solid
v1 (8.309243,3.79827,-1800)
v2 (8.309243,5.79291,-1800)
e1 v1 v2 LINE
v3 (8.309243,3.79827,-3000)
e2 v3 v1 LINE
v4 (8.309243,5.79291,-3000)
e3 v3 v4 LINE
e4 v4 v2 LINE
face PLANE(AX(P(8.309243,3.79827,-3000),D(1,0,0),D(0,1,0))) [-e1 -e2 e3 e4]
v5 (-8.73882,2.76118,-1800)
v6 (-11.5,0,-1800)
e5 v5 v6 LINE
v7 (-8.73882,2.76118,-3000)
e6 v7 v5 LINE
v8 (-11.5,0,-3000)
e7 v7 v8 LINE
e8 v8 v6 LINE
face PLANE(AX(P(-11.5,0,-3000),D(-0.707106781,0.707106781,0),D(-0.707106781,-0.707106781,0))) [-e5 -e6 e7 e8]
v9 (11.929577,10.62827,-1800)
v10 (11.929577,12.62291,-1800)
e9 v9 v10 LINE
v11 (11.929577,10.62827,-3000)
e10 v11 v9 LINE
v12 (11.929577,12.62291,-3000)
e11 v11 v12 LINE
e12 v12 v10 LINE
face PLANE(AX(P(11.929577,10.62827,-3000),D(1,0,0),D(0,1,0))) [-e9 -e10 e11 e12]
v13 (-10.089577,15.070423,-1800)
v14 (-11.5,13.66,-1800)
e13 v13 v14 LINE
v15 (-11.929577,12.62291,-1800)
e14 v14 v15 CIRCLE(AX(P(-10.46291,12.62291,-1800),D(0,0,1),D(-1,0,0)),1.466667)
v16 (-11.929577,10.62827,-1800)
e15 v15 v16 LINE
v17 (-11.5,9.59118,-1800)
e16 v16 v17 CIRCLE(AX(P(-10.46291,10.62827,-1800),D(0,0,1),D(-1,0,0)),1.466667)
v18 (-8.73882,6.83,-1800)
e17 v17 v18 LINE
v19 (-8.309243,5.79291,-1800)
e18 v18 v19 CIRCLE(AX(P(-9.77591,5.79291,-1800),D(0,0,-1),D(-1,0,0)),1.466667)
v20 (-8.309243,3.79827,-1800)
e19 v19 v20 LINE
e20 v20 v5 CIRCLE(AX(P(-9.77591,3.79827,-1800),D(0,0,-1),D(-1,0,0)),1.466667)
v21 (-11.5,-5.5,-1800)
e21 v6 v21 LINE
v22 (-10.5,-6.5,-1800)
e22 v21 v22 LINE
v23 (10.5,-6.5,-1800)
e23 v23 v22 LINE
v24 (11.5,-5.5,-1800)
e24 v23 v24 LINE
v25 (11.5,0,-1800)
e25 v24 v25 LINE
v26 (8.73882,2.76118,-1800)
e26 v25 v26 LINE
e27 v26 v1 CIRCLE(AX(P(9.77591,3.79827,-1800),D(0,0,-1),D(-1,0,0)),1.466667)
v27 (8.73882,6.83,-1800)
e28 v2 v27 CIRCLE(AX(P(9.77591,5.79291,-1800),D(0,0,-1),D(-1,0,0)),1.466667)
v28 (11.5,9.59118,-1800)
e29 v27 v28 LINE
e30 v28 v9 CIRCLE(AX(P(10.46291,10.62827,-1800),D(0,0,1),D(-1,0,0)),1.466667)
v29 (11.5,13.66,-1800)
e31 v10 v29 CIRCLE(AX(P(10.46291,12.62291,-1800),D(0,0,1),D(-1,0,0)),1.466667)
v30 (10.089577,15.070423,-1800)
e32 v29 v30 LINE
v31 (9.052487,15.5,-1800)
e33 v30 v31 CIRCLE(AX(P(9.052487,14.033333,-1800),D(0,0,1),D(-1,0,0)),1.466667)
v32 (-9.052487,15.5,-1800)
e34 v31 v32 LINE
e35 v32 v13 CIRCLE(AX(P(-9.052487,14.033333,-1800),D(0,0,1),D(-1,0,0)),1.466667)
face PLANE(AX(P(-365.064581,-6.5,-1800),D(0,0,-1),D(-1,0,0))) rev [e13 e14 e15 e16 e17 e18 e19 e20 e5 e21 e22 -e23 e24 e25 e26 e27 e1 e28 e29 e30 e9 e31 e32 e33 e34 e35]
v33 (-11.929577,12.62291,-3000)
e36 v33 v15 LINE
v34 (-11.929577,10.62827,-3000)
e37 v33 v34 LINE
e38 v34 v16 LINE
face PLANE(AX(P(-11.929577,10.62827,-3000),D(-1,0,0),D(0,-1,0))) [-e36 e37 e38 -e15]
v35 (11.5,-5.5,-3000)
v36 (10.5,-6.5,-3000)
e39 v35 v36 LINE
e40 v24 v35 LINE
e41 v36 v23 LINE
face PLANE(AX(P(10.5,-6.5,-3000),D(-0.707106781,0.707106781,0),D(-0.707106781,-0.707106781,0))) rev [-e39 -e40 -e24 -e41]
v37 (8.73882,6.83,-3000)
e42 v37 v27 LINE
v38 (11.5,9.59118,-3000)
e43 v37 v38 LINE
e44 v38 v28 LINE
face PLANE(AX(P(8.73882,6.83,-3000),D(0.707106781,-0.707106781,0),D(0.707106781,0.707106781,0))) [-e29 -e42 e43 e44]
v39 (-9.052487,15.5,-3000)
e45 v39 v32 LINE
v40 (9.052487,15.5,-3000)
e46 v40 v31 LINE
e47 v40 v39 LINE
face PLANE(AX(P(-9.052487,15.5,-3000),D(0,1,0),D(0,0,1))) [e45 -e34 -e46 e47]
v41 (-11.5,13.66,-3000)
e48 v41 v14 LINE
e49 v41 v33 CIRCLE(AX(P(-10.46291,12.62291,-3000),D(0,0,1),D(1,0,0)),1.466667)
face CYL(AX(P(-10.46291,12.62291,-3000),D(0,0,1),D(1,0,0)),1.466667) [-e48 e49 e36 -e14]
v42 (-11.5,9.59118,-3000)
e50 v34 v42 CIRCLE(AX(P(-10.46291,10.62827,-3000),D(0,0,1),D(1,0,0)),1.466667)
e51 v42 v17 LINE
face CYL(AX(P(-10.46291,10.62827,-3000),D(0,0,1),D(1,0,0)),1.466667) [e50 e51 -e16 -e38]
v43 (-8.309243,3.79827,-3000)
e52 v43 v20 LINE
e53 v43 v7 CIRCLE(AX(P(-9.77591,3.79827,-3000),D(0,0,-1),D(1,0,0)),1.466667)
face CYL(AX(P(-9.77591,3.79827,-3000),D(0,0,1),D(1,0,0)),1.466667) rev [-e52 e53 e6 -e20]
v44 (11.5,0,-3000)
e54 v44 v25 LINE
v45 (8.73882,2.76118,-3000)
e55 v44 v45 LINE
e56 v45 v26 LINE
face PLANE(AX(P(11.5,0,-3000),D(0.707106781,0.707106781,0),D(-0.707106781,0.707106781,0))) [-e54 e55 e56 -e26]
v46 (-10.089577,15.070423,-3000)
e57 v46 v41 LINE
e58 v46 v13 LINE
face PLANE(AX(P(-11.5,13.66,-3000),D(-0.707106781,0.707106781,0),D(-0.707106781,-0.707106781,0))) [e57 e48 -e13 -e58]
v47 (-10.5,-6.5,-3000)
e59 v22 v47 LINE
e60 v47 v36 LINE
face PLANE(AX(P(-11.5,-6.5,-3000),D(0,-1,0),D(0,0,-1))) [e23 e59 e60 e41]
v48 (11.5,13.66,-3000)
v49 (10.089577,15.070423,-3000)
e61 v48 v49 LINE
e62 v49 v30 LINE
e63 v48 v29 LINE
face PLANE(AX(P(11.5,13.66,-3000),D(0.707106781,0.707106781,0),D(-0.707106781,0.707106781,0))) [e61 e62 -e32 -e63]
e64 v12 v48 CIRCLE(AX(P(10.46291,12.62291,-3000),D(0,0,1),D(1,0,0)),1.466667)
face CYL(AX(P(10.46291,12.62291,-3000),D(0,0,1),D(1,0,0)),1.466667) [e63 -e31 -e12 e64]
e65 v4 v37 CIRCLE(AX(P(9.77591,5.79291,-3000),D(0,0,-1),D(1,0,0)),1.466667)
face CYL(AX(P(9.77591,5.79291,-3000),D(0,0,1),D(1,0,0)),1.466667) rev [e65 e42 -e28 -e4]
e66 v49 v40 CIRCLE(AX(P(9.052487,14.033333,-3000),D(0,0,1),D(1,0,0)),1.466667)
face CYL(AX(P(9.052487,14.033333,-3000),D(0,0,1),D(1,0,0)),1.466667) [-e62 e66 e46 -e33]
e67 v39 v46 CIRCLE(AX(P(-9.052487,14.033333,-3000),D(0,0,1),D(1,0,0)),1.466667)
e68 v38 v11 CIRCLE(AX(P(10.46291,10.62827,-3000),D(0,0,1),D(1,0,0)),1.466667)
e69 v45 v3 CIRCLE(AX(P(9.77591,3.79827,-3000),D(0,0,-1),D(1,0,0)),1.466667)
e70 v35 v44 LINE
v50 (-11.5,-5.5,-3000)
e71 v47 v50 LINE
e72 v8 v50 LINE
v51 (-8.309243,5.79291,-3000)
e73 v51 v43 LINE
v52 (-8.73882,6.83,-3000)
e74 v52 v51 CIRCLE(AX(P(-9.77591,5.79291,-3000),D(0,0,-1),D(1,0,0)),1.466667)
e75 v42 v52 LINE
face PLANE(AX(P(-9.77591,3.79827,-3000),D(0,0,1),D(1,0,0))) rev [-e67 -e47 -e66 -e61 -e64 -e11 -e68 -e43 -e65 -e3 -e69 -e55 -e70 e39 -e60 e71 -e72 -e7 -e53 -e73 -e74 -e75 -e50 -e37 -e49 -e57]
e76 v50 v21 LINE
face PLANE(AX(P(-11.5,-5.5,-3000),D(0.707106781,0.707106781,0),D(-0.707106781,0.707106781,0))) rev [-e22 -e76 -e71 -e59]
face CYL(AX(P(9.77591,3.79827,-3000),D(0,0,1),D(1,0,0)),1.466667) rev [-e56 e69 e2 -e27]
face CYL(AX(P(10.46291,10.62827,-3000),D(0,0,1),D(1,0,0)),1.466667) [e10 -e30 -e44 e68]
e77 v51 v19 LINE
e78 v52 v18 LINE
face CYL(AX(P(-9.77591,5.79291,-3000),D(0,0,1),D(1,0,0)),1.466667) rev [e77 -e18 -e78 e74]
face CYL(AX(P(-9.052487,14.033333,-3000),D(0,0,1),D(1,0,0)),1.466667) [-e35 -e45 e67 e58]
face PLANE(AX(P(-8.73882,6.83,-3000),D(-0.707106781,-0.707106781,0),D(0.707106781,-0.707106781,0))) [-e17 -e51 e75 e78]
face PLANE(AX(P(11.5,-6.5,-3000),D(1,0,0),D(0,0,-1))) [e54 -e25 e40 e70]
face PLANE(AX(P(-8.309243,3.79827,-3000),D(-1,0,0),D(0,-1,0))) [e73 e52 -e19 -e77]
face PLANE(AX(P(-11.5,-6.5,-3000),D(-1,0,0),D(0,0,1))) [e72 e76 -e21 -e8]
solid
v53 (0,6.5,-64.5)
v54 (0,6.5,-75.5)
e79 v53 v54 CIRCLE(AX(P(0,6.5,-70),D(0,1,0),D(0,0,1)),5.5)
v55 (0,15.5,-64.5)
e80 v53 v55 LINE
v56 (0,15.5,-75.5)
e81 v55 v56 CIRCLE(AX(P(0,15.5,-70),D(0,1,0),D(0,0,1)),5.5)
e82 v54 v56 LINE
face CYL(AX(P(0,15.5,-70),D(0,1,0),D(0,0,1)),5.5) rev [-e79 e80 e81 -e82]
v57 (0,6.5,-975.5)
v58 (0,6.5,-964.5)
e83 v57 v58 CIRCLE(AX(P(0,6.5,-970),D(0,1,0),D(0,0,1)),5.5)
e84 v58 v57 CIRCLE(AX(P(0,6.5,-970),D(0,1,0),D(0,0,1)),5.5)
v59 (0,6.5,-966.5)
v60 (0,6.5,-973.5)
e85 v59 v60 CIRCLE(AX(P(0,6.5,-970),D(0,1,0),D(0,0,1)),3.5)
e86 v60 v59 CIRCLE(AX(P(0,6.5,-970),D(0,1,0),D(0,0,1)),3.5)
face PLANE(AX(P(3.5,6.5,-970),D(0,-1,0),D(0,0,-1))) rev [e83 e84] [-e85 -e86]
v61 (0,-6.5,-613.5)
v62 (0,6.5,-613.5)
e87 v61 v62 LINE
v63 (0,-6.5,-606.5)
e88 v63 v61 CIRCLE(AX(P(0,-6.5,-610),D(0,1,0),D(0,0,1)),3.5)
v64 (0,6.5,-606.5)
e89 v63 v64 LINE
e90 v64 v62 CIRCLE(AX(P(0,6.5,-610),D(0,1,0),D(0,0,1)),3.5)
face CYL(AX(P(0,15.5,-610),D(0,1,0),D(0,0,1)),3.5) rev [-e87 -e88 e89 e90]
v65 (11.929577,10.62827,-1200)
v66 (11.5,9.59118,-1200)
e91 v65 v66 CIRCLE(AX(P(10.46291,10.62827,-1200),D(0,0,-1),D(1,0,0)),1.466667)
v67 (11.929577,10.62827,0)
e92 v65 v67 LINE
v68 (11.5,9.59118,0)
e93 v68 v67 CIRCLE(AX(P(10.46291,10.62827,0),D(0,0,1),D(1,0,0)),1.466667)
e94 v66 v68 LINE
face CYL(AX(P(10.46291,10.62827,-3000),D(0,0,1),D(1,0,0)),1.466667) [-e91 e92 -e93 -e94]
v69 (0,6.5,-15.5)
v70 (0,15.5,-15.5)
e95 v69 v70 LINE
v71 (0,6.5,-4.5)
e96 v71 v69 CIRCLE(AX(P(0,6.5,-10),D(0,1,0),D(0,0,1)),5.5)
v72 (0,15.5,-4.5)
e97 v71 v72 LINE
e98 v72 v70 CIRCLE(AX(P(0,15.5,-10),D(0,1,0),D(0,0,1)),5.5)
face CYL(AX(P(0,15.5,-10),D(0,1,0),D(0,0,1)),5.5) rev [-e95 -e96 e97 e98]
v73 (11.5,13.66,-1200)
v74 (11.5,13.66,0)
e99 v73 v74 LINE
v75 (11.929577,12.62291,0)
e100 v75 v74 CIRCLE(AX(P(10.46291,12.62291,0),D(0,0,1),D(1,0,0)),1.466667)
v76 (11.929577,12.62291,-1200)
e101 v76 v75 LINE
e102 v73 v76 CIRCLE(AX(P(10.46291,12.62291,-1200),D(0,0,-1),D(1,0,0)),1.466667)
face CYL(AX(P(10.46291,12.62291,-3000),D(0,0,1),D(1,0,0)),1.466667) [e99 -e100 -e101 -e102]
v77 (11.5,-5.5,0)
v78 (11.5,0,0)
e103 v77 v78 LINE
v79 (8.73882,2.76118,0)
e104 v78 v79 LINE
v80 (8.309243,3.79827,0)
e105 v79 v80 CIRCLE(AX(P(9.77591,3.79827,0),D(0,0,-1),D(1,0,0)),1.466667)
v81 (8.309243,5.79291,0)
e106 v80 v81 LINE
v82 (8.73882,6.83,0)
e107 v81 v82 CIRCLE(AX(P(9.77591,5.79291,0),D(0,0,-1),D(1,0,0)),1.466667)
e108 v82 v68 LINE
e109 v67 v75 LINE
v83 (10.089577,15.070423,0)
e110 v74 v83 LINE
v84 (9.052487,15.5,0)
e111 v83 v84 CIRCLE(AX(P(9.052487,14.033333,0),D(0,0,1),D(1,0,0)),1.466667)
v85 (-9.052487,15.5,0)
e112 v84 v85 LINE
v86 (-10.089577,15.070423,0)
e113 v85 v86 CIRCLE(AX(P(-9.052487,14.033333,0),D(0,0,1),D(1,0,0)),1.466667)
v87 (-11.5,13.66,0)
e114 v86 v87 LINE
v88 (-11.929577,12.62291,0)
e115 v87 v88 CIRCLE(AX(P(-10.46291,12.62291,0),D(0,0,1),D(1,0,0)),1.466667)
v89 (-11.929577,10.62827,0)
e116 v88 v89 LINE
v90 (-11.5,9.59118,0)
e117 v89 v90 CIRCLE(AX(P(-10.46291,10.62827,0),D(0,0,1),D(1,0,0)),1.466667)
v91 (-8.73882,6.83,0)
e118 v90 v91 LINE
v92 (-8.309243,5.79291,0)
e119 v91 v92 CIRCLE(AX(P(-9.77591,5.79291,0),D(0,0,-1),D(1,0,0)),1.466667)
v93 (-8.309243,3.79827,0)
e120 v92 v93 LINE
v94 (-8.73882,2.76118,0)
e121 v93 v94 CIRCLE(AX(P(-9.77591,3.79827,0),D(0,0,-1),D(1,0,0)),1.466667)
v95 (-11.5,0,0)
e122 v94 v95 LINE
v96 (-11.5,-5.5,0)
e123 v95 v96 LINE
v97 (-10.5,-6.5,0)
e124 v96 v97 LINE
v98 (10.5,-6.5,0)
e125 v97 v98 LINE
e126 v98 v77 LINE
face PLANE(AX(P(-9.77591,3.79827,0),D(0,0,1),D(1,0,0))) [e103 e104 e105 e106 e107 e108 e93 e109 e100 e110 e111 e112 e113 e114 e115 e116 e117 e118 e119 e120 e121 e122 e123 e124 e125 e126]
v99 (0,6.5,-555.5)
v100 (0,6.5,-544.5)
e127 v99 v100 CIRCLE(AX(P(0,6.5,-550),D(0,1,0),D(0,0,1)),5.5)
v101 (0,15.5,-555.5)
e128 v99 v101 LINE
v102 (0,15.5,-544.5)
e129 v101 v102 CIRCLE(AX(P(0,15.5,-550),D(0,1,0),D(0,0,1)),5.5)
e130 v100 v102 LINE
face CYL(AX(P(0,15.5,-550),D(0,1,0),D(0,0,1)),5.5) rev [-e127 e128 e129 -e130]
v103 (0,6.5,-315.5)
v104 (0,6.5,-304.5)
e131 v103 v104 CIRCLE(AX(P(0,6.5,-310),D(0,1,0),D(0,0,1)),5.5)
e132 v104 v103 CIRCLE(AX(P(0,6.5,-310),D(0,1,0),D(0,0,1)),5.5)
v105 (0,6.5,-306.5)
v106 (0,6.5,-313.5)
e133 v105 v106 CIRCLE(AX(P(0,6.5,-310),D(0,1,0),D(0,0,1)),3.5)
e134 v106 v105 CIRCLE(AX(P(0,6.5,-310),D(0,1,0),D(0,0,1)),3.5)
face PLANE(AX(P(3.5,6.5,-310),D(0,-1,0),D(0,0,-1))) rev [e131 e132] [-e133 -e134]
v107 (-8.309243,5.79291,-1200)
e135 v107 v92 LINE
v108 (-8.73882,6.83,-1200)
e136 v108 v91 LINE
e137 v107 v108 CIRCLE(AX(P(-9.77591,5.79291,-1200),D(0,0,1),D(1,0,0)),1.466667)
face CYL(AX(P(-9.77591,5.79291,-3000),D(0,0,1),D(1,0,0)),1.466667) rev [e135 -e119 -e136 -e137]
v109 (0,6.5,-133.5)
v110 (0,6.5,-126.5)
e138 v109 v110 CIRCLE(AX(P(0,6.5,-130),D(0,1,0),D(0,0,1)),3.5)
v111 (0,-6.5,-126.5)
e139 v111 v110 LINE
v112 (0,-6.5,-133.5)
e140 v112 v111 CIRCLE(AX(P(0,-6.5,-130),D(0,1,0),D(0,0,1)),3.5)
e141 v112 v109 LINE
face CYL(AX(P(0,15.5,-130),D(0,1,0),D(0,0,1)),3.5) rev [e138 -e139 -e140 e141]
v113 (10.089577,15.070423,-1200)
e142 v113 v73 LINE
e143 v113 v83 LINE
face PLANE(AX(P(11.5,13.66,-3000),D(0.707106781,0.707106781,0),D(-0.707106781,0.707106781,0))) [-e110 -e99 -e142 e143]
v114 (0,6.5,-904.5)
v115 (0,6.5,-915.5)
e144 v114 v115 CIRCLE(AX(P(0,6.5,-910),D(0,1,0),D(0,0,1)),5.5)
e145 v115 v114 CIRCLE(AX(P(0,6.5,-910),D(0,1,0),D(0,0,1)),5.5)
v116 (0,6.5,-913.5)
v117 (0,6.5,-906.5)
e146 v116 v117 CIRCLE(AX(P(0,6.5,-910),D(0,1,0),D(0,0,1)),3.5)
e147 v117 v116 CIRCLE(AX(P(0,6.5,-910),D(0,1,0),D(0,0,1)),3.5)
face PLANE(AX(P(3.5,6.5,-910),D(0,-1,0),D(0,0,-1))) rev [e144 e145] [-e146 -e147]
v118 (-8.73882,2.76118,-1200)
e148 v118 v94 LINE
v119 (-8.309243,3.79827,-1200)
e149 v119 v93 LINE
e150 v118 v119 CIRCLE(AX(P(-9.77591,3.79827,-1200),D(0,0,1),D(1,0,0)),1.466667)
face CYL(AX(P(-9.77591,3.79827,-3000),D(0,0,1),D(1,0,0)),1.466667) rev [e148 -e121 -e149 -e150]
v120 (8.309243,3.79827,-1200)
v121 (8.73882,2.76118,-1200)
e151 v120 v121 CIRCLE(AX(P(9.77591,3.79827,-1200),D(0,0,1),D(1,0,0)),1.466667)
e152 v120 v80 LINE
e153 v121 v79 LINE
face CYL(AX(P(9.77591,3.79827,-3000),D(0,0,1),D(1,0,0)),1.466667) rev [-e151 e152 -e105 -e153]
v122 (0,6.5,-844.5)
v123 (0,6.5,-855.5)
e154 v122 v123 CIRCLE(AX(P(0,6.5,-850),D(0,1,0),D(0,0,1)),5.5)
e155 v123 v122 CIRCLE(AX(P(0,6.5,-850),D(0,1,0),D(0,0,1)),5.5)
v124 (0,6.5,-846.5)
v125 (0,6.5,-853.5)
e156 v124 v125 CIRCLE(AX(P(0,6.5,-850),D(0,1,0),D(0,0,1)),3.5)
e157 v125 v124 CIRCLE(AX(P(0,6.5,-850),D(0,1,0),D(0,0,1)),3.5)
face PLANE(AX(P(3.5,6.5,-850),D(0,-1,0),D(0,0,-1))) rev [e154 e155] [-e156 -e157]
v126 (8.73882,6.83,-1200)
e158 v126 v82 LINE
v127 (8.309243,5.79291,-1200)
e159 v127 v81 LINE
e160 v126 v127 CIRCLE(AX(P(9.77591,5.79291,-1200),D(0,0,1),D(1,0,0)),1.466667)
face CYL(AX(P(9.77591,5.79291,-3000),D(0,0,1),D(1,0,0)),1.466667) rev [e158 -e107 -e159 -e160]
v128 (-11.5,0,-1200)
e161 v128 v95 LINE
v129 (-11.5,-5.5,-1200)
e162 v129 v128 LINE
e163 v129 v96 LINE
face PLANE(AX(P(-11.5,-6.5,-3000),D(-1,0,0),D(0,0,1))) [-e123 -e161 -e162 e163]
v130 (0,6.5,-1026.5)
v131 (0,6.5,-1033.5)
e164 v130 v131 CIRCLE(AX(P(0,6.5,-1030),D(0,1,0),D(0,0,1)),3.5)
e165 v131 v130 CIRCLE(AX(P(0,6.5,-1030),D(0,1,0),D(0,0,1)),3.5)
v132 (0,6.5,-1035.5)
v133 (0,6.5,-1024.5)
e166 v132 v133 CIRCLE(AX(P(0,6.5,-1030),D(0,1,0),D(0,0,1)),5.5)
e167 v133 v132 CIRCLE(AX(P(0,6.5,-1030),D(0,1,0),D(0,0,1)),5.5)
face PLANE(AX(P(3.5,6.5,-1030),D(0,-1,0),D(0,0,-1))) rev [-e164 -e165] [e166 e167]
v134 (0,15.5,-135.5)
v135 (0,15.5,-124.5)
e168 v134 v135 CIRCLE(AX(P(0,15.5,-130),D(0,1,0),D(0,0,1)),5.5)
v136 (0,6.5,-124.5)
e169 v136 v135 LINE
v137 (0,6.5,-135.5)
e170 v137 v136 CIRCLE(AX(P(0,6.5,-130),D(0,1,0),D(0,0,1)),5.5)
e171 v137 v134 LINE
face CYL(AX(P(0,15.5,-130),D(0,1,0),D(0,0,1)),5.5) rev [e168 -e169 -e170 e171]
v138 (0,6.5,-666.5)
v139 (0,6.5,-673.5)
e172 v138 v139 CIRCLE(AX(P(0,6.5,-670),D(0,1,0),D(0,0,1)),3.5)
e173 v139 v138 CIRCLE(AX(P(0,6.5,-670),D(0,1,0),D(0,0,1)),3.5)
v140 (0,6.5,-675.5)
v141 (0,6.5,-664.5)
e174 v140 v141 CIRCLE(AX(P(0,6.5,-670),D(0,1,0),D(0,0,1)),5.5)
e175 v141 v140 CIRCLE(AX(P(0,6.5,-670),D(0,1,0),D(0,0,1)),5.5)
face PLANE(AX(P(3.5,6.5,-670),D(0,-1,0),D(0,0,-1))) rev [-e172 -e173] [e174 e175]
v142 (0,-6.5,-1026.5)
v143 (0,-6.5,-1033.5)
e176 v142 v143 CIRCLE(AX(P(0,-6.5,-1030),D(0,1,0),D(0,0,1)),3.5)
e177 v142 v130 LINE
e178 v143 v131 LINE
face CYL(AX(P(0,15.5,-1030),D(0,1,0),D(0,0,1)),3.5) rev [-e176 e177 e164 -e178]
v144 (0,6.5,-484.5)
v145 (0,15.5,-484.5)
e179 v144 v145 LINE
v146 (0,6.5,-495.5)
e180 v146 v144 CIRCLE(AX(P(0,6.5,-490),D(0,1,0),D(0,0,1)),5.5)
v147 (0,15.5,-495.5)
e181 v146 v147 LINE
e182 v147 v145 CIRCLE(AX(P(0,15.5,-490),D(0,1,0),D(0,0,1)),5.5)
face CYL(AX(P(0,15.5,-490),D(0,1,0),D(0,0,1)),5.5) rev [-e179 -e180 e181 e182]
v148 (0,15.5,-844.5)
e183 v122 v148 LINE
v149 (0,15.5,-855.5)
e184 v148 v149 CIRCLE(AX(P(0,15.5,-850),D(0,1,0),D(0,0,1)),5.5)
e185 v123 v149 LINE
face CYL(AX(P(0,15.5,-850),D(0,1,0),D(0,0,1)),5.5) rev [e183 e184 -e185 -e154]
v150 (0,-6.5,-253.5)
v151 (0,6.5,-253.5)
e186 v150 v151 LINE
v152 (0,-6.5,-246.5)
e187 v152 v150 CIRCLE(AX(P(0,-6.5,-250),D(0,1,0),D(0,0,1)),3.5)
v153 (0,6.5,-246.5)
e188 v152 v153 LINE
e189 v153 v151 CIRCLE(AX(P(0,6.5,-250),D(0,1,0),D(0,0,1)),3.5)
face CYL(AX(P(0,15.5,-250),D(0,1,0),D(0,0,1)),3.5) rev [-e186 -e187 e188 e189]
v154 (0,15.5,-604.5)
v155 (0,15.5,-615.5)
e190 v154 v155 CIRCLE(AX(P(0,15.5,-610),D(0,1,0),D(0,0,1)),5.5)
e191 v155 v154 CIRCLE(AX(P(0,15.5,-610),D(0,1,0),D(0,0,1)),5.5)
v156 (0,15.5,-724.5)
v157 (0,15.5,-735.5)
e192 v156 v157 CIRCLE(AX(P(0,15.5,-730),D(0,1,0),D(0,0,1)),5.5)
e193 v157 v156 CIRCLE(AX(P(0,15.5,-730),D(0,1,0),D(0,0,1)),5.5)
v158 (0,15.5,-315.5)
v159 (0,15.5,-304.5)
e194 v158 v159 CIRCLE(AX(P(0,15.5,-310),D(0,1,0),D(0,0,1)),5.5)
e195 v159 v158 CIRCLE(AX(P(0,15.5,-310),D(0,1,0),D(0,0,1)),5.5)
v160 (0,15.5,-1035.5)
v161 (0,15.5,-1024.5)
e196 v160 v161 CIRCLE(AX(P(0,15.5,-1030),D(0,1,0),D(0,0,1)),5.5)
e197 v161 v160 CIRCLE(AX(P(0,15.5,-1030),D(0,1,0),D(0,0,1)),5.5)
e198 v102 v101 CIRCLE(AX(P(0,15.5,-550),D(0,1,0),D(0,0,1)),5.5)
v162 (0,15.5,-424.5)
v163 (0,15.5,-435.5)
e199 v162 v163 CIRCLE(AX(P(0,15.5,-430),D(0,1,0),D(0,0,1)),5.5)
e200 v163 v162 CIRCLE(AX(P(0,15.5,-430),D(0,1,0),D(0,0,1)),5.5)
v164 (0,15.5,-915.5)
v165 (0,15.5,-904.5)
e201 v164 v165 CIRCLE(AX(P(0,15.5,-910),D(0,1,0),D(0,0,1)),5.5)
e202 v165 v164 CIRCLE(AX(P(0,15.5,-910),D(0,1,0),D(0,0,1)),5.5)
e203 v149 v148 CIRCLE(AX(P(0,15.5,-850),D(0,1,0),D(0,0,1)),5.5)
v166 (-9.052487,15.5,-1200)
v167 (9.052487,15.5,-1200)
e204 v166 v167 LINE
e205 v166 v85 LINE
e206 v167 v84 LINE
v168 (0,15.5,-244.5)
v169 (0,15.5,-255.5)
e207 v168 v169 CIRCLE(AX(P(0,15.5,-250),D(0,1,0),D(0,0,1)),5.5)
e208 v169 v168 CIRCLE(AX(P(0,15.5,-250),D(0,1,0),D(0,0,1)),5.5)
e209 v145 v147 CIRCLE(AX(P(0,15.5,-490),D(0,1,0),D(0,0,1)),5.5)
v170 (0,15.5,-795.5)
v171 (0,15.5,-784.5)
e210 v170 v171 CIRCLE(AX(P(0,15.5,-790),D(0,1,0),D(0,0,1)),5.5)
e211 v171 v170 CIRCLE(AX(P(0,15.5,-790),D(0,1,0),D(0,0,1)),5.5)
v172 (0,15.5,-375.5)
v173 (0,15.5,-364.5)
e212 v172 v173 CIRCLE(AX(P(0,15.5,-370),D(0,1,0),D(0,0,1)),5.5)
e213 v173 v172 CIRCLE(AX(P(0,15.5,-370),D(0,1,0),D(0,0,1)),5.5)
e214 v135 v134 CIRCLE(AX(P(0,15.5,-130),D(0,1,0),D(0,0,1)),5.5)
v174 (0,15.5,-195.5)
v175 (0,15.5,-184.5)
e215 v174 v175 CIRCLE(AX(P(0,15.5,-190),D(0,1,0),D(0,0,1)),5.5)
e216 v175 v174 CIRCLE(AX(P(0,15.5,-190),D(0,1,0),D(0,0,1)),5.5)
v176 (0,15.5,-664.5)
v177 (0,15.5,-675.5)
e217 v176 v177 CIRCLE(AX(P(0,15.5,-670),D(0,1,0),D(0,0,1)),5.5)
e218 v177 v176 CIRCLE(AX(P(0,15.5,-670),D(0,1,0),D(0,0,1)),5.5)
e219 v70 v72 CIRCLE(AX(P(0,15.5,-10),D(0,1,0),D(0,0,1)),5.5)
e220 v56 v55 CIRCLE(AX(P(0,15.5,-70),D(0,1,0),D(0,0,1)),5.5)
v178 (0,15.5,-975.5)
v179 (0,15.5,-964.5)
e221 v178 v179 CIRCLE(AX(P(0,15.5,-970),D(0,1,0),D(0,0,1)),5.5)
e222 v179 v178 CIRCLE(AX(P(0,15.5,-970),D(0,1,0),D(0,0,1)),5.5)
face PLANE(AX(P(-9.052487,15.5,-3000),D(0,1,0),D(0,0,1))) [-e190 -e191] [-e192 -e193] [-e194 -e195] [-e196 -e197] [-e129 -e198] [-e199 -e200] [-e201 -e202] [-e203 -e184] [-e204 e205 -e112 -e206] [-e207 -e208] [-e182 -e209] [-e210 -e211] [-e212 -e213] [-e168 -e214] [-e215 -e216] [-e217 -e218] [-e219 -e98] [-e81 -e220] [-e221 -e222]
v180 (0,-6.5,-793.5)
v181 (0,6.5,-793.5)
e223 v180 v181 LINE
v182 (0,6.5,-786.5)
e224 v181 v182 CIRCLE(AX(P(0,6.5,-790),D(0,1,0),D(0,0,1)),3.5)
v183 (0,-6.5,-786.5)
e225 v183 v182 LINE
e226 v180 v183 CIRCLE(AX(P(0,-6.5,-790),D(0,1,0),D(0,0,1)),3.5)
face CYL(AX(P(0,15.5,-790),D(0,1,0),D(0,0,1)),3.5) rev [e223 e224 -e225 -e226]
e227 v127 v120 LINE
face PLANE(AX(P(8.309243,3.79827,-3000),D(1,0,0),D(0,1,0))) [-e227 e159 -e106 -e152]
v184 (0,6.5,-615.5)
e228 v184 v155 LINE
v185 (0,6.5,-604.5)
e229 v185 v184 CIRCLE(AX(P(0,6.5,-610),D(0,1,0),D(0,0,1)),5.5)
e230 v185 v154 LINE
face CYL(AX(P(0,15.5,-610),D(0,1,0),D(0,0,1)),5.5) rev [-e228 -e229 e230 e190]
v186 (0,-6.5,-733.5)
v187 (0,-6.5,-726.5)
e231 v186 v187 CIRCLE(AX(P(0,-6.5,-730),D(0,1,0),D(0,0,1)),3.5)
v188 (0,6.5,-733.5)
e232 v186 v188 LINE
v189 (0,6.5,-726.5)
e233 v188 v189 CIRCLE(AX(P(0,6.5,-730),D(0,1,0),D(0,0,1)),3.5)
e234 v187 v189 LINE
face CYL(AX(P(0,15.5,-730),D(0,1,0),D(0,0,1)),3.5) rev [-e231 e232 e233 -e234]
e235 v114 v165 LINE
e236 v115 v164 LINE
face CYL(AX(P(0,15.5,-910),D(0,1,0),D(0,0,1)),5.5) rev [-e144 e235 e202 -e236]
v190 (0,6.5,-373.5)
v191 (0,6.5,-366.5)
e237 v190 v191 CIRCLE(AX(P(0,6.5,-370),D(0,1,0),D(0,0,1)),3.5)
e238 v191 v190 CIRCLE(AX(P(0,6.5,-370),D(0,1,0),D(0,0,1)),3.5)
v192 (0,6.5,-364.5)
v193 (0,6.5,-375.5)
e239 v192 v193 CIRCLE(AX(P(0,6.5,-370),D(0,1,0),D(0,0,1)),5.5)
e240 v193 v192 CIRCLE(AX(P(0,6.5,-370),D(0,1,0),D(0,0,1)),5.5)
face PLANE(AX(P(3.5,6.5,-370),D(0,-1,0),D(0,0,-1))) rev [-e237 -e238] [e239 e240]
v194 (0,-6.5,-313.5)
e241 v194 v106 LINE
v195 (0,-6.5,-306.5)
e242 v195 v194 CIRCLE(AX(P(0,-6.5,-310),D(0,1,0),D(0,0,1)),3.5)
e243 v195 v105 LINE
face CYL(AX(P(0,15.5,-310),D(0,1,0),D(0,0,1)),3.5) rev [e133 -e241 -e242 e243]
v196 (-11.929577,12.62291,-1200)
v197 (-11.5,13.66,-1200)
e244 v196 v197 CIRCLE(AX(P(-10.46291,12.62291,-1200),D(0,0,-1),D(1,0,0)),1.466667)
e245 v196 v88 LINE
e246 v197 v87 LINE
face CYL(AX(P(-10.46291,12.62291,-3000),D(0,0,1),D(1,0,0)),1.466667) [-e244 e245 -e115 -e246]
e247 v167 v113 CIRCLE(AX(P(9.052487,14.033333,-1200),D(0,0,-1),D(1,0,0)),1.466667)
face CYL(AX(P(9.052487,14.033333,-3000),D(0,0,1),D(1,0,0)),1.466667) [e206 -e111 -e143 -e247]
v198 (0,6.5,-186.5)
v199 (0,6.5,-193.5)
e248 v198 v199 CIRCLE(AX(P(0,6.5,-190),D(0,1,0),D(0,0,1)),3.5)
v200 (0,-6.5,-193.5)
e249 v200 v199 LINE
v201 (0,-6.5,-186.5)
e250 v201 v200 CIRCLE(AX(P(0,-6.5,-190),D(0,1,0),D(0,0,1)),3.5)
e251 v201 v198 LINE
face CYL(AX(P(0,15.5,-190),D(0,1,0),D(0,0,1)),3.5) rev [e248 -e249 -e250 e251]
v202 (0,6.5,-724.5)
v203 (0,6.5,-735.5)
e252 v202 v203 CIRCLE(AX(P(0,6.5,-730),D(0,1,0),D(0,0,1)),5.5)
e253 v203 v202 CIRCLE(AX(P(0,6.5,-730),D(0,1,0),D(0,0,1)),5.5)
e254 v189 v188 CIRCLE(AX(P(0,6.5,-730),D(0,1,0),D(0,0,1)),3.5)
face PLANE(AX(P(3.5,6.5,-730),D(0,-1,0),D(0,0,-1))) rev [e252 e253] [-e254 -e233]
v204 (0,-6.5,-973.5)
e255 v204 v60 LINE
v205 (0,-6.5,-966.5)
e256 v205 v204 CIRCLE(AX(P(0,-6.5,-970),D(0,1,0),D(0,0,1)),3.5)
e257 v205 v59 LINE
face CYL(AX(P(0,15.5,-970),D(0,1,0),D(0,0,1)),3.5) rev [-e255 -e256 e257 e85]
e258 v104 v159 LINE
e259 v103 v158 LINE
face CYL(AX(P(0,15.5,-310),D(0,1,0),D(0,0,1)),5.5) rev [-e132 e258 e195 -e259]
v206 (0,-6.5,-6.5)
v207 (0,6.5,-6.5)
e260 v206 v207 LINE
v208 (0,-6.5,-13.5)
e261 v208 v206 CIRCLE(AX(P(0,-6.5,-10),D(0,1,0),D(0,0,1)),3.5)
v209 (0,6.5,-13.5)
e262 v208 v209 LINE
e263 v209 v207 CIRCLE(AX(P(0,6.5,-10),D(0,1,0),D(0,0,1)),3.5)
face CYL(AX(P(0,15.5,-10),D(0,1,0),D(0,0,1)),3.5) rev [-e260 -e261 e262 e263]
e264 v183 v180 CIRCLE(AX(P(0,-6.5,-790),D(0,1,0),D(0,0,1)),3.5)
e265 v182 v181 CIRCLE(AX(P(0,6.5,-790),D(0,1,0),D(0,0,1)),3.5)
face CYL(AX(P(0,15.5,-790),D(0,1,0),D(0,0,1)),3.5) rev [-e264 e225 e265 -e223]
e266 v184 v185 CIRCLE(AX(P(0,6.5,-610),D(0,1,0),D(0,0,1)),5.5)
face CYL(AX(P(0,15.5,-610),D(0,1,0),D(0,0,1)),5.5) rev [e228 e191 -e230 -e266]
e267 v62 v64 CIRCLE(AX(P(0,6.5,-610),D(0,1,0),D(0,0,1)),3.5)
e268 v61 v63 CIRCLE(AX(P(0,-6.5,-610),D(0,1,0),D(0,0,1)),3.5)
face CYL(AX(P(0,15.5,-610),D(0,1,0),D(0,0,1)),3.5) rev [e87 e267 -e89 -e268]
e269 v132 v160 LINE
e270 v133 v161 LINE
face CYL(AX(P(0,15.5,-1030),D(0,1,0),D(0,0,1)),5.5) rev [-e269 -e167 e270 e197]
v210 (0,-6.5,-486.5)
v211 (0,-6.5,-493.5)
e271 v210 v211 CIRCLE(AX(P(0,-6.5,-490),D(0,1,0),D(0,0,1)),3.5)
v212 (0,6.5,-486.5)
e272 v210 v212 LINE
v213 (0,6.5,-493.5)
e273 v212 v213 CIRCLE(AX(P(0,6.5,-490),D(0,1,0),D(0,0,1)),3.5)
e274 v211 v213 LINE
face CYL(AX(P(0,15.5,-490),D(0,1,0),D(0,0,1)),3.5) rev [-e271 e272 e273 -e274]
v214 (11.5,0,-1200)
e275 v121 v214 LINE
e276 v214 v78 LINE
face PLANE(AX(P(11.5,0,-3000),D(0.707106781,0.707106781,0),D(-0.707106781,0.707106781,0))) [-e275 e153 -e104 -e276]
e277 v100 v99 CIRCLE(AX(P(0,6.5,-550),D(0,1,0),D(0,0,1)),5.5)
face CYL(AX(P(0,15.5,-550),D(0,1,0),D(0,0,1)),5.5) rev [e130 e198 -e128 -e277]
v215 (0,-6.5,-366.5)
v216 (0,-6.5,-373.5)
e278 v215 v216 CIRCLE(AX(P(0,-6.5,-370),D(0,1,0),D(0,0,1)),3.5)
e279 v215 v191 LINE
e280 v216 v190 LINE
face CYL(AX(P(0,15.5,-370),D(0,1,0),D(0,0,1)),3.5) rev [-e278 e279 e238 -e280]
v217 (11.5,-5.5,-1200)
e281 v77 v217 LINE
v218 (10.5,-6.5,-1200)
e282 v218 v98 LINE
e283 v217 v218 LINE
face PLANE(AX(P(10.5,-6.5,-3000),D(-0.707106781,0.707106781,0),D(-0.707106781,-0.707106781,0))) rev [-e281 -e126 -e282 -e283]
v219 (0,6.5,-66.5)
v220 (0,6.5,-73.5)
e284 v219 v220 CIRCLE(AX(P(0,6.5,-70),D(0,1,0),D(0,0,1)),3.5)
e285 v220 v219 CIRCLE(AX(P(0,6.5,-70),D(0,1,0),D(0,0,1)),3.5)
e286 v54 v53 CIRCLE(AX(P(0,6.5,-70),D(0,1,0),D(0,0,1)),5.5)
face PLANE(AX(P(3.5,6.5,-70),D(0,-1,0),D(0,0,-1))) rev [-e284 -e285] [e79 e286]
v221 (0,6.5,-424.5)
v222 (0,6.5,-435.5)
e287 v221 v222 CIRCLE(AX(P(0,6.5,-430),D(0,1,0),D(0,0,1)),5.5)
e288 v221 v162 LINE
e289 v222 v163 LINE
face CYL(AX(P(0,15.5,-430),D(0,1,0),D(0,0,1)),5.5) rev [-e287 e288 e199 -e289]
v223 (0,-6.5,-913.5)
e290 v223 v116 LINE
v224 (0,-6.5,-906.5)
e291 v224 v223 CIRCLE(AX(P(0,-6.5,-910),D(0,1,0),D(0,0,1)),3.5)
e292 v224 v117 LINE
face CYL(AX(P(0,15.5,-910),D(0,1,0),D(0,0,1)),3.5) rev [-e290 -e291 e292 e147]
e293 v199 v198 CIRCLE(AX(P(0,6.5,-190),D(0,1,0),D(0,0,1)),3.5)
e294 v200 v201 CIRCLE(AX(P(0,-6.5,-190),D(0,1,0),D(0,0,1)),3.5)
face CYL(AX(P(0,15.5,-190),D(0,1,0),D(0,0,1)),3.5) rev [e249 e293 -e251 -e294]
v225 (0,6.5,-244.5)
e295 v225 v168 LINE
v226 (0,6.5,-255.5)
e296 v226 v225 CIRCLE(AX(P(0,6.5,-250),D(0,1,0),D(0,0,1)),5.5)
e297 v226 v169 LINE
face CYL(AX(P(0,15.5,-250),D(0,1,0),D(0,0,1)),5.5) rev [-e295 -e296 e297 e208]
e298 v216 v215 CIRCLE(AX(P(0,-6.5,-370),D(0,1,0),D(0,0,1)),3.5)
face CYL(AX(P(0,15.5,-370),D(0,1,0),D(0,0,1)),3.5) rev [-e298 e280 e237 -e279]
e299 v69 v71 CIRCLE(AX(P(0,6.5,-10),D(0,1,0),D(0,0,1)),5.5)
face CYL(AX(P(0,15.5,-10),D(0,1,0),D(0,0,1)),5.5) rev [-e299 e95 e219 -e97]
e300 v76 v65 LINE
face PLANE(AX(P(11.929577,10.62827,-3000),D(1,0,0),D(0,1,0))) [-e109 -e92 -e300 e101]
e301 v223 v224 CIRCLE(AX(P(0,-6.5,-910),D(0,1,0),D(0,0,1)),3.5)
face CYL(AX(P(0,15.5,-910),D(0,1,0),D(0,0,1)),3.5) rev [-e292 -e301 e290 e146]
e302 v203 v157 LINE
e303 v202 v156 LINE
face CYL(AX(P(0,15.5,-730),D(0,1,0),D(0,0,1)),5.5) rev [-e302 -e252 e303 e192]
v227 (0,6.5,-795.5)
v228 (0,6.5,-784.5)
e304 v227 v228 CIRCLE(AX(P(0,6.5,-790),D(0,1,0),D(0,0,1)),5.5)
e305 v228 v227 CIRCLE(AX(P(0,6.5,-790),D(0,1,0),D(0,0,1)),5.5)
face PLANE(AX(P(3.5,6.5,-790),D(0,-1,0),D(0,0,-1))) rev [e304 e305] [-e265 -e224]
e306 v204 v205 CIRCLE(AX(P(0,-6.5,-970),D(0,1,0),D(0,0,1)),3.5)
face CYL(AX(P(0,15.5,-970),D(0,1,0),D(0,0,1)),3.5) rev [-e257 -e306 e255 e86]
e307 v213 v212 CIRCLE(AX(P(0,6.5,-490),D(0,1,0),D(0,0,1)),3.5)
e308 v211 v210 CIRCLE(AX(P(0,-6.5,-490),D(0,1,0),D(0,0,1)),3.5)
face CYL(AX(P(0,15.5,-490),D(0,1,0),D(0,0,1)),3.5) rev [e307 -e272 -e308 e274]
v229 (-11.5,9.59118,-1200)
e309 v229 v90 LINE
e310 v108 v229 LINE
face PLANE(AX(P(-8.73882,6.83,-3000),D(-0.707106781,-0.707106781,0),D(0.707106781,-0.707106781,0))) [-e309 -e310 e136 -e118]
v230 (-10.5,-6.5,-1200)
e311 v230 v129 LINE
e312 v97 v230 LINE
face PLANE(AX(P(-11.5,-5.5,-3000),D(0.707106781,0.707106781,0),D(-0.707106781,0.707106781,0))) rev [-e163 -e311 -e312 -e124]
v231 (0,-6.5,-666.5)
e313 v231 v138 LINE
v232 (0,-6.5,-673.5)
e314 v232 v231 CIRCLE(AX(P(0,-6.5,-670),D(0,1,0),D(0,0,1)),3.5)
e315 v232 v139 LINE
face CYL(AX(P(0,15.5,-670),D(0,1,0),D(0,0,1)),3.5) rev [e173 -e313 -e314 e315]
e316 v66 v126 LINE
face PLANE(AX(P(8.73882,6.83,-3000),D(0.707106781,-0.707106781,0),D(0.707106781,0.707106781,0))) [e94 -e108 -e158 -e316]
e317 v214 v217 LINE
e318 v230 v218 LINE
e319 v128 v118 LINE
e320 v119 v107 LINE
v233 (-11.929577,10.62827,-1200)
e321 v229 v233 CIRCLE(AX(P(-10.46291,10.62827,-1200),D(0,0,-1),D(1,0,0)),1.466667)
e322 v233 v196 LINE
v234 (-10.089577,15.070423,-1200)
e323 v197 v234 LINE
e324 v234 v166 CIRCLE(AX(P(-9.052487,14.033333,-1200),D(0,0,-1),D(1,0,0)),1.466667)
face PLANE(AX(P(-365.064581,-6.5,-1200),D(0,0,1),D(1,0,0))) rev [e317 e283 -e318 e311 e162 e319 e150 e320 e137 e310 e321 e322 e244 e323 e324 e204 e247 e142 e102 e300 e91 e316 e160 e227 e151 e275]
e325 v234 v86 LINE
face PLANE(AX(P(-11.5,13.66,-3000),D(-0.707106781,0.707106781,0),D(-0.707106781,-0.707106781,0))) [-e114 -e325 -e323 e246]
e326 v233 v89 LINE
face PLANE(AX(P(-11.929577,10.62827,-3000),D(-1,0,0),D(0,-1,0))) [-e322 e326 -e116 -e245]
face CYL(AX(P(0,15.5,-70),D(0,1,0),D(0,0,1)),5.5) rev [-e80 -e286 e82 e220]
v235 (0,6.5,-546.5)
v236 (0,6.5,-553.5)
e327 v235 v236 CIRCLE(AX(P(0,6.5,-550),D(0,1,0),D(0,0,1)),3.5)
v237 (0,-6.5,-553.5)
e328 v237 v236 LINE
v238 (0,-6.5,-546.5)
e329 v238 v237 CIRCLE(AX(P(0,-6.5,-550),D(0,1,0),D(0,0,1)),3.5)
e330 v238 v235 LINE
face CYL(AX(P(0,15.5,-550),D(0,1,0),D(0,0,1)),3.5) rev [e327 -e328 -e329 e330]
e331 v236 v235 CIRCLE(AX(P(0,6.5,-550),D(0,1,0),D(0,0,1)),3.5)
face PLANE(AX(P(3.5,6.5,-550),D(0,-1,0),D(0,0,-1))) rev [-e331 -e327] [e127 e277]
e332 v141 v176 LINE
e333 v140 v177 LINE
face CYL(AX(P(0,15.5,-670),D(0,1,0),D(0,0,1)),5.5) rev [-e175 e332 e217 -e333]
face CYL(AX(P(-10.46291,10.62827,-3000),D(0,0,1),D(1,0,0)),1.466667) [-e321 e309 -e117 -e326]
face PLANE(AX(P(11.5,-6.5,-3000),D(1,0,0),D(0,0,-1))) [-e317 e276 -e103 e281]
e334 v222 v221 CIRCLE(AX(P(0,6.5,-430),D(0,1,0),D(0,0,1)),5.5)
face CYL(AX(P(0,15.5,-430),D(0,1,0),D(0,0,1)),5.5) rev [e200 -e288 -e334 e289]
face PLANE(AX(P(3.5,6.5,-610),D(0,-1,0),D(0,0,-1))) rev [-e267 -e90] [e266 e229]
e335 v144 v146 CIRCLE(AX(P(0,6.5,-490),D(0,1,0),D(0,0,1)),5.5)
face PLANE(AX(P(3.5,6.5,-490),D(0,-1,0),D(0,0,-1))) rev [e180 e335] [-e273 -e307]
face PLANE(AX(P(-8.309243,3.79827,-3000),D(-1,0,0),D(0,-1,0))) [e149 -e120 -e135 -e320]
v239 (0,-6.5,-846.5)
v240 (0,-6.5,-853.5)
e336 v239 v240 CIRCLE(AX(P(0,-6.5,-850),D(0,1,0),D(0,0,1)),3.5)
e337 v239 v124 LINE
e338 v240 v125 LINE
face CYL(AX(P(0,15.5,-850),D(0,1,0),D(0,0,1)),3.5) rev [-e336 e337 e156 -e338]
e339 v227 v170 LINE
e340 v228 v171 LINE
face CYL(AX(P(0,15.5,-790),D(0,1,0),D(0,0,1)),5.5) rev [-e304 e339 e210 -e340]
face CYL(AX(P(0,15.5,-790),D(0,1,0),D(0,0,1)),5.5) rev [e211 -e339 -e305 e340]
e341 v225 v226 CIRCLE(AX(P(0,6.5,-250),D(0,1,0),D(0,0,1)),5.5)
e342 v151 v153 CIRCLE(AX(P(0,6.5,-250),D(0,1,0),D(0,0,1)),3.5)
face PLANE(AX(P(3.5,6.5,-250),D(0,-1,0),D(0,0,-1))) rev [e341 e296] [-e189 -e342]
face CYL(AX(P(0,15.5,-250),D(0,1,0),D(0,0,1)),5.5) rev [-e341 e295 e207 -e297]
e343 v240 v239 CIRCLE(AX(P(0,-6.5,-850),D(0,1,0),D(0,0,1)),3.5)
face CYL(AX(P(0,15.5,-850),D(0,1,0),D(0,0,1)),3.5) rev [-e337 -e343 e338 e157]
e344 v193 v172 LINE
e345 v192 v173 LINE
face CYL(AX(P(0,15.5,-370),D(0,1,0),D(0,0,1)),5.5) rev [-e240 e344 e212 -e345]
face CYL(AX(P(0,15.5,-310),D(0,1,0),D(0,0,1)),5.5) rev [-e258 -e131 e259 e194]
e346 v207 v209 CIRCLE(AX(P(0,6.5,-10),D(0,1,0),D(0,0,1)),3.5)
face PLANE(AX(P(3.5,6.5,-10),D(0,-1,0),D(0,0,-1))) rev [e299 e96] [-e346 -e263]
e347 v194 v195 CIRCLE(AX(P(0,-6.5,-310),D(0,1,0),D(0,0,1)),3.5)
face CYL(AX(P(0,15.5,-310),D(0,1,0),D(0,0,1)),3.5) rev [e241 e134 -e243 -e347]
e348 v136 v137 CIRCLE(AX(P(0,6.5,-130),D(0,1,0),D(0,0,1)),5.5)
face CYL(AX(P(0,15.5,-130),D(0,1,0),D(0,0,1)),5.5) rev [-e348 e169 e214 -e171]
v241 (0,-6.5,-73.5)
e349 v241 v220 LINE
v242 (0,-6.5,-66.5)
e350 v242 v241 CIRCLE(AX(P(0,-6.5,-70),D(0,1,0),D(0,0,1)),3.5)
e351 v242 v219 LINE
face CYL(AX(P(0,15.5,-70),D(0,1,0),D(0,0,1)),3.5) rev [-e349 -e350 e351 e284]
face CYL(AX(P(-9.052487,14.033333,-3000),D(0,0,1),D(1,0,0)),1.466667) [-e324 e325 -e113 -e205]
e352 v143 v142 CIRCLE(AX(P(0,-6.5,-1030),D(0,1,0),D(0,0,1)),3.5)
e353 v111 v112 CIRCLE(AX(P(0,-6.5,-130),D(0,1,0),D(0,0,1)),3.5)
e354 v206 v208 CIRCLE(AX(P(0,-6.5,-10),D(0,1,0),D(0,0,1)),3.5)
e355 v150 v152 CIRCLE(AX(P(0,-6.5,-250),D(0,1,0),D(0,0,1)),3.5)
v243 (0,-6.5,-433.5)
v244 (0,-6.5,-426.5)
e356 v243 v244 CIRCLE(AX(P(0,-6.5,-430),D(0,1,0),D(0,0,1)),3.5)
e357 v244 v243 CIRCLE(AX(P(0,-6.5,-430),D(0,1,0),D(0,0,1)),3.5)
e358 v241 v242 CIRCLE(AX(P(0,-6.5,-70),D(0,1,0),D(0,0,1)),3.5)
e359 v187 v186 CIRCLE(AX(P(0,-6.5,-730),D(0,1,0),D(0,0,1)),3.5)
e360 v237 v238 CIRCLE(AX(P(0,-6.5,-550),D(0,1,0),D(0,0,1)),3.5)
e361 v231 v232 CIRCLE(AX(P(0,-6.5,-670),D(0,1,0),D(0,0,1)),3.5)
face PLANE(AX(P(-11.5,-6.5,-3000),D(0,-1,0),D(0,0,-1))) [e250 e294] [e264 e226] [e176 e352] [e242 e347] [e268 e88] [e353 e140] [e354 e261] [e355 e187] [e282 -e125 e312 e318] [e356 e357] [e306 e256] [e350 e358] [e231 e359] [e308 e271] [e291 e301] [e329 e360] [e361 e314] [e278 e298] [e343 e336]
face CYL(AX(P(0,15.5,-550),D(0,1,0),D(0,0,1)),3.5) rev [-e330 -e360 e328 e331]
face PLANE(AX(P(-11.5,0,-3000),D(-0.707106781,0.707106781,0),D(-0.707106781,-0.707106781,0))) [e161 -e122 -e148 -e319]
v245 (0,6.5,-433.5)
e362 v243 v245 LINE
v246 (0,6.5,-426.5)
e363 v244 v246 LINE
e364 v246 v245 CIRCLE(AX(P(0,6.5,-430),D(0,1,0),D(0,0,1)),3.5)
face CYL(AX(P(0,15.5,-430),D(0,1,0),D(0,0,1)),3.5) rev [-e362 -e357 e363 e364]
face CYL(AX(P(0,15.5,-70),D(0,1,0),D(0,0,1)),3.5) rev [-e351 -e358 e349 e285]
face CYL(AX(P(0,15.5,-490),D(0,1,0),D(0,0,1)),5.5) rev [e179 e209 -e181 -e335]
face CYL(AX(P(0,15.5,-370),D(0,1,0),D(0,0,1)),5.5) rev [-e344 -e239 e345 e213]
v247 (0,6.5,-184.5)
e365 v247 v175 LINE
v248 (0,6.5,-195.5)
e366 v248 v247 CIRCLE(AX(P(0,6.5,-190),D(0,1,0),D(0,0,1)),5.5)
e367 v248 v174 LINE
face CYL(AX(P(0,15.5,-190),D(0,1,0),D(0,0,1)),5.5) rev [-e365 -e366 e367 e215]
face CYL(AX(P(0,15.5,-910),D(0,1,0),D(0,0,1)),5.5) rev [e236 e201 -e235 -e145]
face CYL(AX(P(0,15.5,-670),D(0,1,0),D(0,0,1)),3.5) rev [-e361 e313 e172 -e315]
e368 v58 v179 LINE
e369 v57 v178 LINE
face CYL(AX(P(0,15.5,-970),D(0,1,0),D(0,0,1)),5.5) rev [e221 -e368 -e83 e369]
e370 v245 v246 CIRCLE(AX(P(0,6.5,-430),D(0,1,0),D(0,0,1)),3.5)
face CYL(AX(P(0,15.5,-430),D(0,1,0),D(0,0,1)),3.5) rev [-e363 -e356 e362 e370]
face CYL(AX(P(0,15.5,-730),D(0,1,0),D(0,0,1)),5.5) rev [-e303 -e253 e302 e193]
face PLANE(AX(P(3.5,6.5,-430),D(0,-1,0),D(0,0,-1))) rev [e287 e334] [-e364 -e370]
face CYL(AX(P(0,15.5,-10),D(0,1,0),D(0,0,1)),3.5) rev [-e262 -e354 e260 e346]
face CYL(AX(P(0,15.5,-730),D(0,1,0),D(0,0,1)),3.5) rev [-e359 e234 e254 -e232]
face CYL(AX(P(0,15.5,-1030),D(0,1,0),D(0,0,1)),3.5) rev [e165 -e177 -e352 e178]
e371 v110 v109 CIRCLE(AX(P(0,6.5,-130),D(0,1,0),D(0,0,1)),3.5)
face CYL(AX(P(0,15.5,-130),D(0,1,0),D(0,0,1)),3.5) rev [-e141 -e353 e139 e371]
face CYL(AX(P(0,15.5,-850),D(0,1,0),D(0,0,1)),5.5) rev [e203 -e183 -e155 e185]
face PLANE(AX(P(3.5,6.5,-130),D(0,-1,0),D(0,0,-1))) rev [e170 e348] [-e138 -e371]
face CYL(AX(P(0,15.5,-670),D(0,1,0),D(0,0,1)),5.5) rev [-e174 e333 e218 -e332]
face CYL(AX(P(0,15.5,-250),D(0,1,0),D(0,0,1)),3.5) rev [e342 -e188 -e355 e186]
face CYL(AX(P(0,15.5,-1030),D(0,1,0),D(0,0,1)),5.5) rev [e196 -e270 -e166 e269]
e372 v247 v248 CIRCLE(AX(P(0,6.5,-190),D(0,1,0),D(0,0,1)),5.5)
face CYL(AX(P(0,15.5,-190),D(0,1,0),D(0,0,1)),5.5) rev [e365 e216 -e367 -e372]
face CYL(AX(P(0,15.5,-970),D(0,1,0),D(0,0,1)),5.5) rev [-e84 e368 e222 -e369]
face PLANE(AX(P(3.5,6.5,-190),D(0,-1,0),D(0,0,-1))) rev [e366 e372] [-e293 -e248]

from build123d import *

# Parameters (mm, degrees)
BOSS_EXTRUDE1_DEPTH           = 3000
COUNTERBORE_HOLE1_D           = 7
COUNTERBORE_HOLE1_CBORE_D     = 11
COUNTERBORE_HOLE1_CBORE_DEPTH = 9
LPATTERN1_COUNT               = 18
LPATTERN1_PITCH               = 60
CHAMFER1_SIZE                 = 1
SKETCH7_W                     = 717.319877582
SKETCH7_H                     = 600
CUT_EXTRUDE1_DEPTH            = 3001.104383984


with BuildPart() as part:
    # Sketch3 → Boss-Extrude1 (new body)
    with BuildSketch(Plane.XY):
        with BuildLine():
            Line((-11.5, -6.5), (11.5, -6.5))
            Line((11.5, -6.5), (11.5, 0))
            Line((11.5, 0), (8.738819621, 2.761180379))
            ThreePointArc((8.738819621, 2.761180379), (8.420886253, 3.23700129), (8.309242901, 3.798270324))
            Line((8.309242901, 3.798270324), (8.309242901, 5.792910054))
            ThreePointArc((8.309242901, 5.792910054), (8.420886253, 6.354179088), (8.738819621, 6.83))
            Line((8.738819621, 6.83), (11.5, 9.591180379))
            ThreePointArc((11.5, 9.591180379), (11.817933369, 10.06700129), (11.929576721, 10.628270324))
            Line((11.929576721, 10.628270324), (11.929576721, 12.622910054))
            ThreePointArc((11.929576721, 12.622910054), (11.817933369, 13.184179088), (11.5, 13.66))
            Line((11.5, 13.66), (10.089576721, 15.070423279))
            ThreePointArc((10.089576721, 15.070423279), (9.613755809, 15.388356648), (9.052486775, 15.5))
            Line((9.052486775, 15.5), (-9.052486775, 15.5))
            ThreePointArc((-9.052486775, 15.5), (-9.613755809, 15.388356648), (-10.089576721, 15.070423279))
            Line((-10.089576721, 15.070423279), (-11.5, 13.66))
            ThreePointArc((-11.5, 13.66), (-11.817933369, 13.184179088), (-11.929576721, 12.622910054))
            Line((-11.929576721, 12.622910054), (-11.929576721, 10.628270324))
            ThreePointArc((-11.929576721, 10.628270324), (-11.817933369, 10.06700129), (-11.5, 9.591180379))
            Line((-11.5, 9.591180379), (-8.738819621, 6.83))
            ThreePointArc((-8.738819621, 6.83), (-8.420886253, 6.354179088), (-8.309242901, 5.792910054))
            Line((-8.309242901, 5.792910054), (-8.309242901, 3.798270324))
            ThreePointArc((-8.309242901, 3.798270324), (-8.420886253, 3.23700129), (-8.738819621, 2.761180379))
            Line((-8.738819621, 2.761180379), (-11.5, 0))
            Line((-11.5, 0), (-11.5, -6.5))
        make_face()
    extrude(amount=-BOSS_EXTRUDE1_DEPTH)

    # Counterbore Hole1 (through all)
    with Locations(Plane(origin=(0, 15.5, 0), x_dir=(-1, 0, 0), z_dir=(0, 1, 0))):
        with Locations((0, -10)):
            counterbore_hole1 = CounterBoreHole(COUNTERBORE_HOLE1_D / 2, COUNTERBORE_HOLE1_CBORE_D / 2, COUNTERBORE_HOLE1_CBORE_DEPTH)

    # LPattern1: Counterbore Hole1 ×18
    with Locations(*[(0, 0, -i * LPATTERN1_PITCH) for i in range(1, LPATTERN1_COUNT)]):
        add(counterbore_hole1, mode=Mode.SUBTRACT)

    # Chamfer1
    chamfer1_edges = [part.edges().sort_by_distance(p)[0] for p in [
        (11.5, -6.5, -1500),
        (-11.5, -6.5, -1500),
    ]]
    chamfer(chamfer1_edges, length=CHAMFER1_SIZE)

    # Sketch7 → Cut-Extrude1 (cut, through all)
    with BuildSketch(Plane(origin=(0, 15.5, 0), x_dir=(1, 0, 0), z_dir=(0, 1, 0))):
        with Locations((-6.404641764, 1500)):
            Rectangle(SKETCH7_W, SKETCH7_H)
    extrude(amount=-CUT_EXTRUDE1_DEPTH, mode=Mode.SUBTRACT)


with BuildPart() as cut_extrude1_piece_1:
    # of the separate pieces the step leaves, piece 1, a body of its own (cut_extrude1_pieces)
    add(part.part.solids().sort_by_distance((-11.5, -5.5, -1800))[0])


with BuildPart() as cut_extrude1_piece_2:
    # of the separate pieces the step leaves, piece 2, a body of its own (cut_extrude1_pieces)
    add(part.part.solids().sort_by_distance((-11.5, -5.5, 0))[0])


solid = Compound([cut_extrude1_piece_1.part, cut_extrude1_piece_2.part])
